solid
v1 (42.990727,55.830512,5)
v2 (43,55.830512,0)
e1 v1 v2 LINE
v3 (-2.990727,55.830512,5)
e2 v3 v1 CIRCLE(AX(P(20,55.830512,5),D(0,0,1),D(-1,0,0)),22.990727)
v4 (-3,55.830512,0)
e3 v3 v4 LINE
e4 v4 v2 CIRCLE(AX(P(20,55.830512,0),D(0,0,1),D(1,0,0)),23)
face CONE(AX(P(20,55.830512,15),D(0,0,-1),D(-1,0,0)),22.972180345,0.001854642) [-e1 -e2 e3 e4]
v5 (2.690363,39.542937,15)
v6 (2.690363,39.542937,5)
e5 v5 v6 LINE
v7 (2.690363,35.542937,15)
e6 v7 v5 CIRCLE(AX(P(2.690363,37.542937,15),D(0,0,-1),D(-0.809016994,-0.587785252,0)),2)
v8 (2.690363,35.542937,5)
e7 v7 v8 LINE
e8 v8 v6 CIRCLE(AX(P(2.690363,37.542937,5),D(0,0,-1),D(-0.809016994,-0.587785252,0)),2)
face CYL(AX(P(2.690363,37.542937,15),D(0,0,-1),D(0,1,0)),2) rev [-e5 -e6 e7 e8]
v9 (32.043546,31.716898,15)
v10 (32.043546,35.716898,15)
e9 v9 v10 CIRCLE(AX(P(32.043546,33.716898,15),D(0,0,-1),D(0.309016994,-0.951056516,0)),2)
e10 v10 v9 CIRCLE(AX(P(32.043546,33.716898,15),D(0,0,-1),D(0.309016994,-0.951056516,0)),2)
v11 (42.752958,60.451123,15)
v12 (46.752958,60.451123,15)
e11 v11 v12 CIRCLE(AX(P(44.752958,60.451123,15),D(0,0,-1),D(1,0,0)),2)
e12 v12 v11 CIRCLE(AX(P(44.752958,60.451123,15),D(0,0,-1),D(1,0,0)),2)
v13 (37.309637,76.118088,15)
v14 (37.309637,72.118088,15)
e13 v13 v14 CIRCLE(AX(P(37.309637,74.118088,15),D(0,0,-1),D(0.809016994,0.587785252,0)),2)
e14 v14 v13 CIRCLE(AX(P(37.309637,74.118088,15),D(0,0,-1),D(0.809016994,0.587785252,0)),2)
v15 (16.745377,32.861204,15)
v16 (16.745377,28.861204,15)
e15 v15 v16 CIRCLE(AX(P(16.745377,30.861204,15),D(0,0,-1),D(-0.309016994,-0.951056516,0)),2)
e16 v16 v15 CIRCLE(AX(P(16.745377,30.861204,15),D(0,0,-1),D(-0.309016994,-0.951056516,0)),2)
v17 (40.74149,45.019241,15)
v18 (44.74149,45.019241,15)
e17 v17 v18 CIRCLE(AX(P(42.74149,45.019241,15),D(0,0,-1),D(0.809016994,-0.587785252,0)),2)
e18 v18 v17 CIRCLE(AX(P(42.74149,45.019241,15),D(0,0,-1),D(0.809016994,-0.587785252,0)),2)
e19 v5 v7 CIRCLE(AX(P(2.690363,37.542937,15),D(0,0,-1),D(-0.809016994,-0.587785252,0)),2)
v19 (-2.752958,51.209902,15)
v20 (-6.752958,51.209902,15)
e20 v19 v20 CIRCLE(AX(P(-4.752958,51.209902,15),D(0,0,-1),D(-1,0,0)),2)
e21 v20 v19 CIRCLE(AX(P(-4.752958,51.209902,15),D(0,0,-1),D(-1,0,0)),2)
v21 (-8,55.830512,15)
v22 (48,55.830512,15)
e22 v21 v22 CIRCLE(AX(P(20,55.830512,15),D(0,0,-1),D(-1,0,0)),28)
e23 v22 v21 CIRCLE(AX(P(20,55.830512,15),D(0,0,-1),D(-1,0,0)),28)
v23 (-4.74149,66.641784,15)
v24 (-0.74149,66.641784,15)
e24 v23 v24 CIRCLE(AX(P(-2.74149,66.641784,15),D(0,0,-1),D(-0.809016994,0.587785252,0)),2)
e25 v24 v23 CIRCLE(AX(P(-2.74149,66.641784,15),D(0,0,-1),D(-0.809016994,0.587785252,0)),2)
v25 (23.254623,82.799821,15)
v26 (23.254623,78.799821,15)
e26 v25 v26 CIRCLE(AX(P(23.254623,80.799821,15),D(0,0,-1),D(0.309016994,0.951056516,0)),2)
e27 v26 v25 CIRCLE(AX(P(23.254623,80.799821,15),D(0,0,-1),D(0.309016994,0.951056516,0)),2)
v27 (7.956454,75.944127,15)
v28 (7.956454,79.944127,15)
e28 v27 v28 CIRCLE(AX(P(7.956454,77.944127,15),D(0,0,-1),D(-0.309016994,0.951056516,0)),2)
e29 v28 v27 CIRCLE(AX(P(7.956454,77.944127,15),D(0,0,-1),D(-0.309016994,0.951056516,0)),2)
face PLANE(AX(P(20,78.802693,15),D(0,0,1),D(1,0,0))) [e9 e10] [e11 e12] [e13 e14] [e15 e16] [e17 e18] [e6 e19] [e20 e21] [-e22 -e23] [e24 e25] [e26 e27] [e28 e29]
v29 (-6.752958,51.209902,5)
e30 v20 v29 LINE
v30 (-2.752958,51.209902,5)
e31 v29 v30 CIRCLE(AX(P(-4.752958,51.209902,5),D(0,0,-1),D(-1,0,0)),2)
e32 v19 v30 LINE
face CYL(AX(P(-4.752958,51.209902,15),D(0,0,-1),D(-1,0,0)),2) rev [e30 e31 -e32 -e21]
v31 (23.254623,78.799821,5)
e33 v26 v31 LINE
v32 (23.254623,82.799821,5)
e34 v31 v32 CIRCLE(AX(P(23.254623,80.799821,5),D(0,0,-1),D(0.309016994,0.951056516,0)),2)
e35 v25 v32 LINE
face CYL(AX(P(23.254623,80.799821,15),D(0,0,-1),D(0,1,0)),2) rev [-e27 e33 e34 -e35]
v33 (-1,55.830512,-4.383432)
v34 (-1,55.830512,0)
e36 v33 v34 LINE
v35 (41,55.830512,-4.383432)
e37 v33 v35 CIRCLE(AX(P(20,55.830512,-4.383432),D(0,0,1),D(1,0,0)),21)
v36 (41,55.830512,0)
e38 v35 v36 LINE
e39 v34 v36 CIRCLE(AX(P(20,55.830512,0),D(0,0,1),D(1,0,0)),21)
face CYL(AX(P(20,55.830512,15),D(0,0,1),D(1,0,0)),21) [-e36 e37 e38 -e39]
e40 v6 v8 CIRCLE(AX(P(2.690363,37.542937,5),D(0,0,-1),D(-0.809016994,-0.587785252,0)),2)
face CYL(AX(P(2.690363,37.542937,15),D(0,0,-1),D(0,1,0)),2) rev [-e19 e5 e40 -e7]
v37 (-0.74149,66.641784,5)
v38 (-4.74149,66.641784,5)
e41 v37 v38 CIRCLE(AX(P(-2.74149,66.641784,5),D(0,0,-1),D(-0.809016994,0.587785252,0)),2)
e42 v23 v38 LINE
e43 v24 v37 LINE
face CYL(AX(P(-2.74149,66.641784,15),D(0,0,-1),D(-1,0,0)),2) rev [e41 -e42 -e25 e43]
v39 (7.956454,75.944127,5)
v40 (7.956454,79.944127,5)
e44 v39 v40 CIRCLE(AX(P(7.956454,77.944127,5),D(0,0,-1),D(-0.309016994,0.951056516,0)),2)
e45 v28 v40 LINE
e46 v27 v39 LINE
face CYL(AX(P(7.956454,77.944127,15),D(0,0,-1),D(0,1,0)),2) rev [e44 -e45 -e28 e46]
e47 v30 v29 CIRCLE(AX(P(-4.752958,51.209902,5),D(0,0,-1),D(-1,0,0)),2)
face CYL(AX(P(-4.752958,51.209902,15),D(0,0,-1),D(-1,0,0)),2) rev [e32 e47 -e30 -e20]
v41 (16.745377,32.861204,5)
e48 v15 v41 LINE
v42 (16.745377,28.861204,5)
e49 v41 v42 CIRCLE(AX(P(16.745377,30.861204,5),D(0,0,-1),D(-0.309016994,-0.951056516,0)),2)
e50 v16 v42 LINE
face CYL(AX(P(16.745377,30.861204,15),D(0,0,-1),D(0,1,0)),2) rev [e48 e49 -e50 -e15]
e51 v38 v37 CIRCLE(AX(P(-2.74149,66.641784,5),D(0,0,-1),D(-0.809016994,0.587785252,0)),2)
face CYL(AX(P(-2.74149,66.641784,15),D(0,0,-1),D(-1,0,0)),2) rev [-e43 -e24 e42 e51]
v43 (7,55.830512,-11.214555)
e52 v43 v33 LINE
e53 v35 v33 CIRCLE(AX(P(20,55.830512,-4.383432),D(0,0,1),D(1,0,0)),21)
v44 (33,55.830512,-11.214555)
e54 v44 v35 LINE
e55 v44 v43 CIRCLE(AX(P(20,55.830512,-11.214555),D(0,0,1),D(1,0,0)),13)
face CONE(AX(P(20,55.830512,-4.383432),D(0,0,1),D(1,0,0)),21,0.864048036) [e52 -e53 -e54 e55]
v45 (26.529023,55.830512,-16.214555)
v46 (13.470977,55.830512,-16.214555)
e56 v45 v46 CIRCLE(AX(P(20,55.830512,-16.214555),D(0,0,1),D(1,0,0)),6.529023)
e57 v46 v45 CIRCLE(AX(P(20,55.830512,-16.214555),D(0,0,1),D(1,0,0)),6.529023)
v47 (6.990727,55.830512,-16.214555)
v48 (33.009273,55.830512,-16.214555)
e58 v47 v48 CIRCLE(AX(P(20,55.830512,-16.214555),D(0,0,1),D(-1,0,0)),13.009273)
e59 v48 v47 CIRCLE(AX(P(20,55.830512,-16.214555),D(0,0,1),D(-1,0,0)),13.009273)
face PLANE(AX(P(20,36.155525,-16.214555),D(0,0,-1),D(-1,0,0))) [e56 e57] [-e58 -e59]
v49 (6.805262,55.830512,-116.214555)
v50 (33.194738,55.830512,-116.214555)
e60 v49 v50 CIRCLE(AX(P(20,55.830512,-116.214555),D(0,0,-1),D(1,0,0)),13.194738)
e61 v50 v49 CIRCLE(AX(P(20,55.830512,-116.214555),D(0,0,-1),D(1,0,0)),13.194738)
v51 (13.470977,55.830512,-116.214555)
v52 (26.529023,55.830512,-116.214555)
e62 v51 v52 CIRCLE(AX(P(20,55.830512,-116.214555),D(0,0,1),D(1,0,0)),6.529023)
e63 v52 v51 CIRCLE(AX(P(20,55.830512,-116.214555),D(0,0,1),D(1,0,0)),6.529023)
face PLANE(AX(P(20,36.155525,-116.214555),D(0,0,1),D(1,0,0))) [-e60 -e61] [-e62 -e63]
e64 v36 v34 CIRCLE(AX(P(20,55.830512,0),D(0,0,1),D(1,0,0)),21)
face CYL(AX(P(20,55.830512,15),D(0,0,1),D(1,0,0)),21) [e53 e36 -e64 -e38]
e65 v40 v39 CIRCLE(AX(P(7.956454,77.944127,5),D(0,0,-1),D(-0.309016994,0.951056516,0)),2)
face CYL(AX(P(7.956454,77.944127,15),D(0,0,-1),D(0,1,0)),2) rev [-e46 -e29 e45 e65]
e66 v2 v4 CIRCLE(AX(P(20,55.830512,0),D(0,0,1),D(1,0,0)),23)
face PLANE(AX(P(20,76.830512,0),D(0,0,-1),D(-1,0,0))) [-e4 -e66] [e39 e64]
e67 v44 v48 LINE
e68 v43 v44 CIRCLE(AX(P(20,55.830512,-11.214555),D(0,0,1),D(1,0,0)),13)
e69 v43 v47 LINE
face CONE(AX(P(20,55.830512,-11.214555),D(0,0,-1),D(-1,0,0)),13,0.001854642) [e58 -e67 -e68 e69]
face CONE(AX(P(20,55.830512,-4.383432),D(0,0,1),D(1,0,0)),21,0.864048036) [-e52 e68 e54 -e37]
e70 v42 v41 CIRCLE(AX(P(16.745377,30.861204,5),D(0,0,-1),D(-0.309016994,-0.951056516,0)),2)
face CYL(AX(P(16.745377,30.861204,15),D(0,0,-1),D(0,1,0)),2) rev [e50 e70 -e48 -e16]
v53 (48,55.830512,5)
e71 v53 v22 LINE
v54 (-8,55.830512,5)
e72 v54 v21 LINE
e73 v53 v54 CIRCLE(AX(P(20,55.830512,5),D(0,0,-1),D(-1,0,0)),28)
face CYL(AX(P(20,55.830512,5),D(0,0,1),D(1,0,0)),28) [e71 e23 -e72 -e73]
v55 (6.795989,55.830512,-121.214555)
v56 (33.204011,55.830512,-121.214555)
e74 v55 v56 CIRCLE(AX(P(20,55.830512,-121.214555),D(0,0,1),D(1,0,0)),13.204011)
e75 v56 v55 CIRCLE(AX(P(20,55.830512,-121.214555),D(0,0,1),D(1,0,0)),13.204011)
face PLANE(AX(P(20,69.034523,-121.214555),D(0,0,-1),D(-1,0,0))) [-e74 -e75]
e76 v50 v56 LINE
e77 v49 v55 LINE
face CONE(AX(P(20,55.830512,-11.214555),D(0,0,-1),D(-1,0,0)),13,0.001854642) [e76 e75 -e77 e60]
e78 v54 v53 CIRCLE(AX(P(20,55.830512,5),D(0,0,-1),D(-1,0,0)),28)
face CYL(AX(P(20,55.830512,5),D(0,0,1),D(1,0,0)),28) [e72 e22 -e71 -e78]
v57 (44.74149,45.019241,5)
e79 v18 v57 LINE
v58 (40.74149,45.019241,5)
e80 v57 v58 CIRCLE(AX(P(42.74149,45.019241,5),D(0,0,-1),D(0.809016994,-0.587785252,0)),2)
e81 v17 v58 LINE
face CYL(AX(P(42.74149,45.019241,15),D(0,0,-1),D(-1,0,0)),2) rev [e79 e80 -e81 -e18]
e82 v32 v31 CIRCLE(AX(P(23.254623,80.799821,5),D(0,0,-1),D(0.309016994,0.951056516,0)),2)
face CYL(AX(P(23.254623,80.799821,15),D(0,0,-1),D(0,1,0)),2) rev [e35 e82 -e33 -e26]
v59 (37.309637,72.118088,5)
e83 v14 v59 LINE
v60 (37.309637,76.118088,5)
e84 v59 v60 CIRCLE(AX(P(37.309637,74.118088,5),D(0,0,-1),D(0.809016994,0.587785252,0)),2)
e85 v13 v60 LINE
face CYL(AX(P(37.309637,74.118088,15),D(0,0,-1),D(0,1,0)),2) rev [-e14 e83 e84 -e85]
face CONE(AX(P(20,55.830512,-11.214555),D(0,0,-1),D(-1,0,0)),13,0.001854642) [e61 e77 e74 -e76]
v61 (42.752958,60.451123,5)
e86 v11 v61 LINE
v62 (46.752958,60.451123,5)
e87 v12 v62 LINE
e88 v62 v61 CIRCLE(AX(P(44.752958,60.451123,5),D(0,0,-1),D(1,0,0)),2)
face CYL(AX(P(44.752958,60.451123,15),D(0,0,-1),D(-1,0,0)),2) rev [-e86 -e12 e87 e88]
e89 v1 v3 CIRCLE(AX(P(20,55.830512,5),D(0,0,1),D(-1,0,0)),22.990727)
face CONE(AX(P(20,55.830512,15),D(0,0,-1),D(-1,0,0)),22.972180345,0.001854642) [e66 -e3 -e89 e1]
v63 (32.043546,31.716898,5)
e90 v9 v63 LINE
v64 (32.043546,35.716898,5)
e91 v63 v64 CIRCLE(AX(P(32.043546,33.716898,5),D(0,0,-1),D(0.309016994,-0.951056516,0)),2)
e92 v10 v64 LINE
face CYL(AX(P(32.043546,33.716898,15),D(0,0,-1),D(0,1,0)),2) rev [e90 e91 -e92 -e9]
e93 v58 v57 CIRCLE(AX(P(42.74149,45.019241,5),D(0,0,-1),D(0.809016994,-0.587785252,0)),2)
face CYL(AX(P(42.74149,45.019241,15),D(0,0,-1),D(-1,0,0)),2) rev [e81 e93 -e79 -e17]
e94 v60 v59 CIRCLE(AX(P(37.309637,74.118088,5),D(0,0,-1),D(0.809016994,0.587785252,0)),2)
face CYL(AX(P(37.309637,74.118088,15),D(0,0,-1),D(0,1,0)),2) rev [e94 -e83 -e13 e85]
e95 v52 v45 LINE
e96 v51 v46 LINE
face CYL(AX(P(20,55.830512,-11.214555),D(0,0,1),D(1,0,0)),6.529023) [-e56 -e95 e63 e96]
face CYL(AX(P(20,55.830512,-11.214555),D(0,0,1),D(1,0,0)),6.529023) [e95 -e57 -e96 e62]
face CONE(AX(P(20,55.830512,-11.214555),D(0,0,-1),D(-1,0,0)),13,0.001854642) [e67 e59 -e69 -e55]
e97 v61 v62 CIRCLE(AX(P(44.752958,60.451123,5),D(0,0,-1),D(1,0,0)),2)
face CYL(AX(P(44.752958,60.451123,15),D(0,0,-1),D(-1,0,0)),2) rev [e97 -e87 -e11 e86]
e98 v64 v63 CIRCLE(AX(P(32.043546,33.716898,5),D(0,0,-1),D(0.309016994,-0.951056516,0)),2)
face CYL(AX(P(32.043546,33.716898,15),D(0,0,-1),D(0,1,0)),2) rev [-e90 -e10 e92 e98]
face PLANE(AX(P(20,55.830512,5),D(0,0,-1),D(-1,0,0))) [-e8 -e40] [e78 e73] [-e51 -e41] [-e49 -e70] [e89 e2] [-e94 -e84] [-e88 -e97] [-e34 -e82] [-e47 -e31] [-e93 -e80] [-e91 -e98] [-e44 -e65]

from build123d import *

# Parameters (mm, degrees)
SKETCH5_W           = 13.145964729
SKETCH5_H           = 100
SKETCH6_R           = 28
BOSS_EXTRUDE1_DEPTH = 10
SKETCH7_R           = 2
CUT_EXTRUDE1_DEPTH  = 10
CIRPATTERN1_COUNT   = 10


with BuildPart() as part:
    # Sketch4 → Revolve1 (revolve)
    with BuildSketch(Plane(origin=(20, 0, 0), x_dir=(0, -1, 0), z_dir=(-1, 0, 0)), mode=Mode.PRIVATE) as revolve1_sk:
        Polygon((-76.830512452, 0), (-76.830512452, -4.383431838), (-68.830512452, -11.214554774), (-69.034523253, -121.214554774), (-55.830512452, -121.214554774), (-55.830512452, 15), (-78.802692797, 15), (-78.830512452, 0), align=None)
    revolve(revolve1_sk.sketch.rotate(Axis((20, 55.830512452, 15), (0, 0, -1)), 90), axis=Axis((20, 55.830512452, 15), (0, 0, -1)))

    # Sketch5 → Cut-Revolve1 (revolve, cut)
    with BuildSketch(Plane(origin=(20, 0, 0), x_dir=(0, -1, 0), z_dir=(-1, 0, 0)), mode=Mode.PRIVATE) as cut_revolve1_sk:
        with Locations((-42.728507052, -66.214554774)):
            Rectangle(SKETCH5_W, SKETCH5_H)
    revolve(cut_revolve1_sk.sketch.rotate(Axis((20, 55.830512452, -11.214554774), (0, 0, -1)), 270), axis=Axis((20, 55.830512452, -11.214554774), (0, 0, -1)), mode=Mode.SUBTRACT)

    # Sketch6 → Boss-Extrude1 (add)
    with BuildSketch(Plane(origin=(0, 0, 15), x_dir=(-1, 0, 0), z_dir=(0, 0, -1))):
        with Locations((-20, 55.830512452)):
            Circle(SKETCH6_R)
    extrude(amount=BOSS_EXTRUDE1_DEPTH)

    # Sketch7 → Cut-Extrude1 (cut)
    with BuildSketch(Plane(origin=(0, 0, 5), x_dir=(-1, 0, 0), z_dir=(0, 0, -1))):
        with Locations((4.75295766, 51.209902338)):
            Circle(SKETCH7_R)
    cut_extrude1 = extrude(amount=-CUT_EXTRUDE1_DEPTH, mode=Mode.SUBTRACT)

    # CirPattern1: Cut-Extrude1 ×10 about axis
    cirpattern1_axis = Axis((20, 55.830512452, 0), (0, 0, 1))
    for i in range(1, CIRPATTERN1_COUNT):
        add(cut_extrude1.rotate(cirpattern1_axis, i * 360 / CIRPATTERN1_COUNT), mode=Mode.SUBTRACT)


solid = part.part
